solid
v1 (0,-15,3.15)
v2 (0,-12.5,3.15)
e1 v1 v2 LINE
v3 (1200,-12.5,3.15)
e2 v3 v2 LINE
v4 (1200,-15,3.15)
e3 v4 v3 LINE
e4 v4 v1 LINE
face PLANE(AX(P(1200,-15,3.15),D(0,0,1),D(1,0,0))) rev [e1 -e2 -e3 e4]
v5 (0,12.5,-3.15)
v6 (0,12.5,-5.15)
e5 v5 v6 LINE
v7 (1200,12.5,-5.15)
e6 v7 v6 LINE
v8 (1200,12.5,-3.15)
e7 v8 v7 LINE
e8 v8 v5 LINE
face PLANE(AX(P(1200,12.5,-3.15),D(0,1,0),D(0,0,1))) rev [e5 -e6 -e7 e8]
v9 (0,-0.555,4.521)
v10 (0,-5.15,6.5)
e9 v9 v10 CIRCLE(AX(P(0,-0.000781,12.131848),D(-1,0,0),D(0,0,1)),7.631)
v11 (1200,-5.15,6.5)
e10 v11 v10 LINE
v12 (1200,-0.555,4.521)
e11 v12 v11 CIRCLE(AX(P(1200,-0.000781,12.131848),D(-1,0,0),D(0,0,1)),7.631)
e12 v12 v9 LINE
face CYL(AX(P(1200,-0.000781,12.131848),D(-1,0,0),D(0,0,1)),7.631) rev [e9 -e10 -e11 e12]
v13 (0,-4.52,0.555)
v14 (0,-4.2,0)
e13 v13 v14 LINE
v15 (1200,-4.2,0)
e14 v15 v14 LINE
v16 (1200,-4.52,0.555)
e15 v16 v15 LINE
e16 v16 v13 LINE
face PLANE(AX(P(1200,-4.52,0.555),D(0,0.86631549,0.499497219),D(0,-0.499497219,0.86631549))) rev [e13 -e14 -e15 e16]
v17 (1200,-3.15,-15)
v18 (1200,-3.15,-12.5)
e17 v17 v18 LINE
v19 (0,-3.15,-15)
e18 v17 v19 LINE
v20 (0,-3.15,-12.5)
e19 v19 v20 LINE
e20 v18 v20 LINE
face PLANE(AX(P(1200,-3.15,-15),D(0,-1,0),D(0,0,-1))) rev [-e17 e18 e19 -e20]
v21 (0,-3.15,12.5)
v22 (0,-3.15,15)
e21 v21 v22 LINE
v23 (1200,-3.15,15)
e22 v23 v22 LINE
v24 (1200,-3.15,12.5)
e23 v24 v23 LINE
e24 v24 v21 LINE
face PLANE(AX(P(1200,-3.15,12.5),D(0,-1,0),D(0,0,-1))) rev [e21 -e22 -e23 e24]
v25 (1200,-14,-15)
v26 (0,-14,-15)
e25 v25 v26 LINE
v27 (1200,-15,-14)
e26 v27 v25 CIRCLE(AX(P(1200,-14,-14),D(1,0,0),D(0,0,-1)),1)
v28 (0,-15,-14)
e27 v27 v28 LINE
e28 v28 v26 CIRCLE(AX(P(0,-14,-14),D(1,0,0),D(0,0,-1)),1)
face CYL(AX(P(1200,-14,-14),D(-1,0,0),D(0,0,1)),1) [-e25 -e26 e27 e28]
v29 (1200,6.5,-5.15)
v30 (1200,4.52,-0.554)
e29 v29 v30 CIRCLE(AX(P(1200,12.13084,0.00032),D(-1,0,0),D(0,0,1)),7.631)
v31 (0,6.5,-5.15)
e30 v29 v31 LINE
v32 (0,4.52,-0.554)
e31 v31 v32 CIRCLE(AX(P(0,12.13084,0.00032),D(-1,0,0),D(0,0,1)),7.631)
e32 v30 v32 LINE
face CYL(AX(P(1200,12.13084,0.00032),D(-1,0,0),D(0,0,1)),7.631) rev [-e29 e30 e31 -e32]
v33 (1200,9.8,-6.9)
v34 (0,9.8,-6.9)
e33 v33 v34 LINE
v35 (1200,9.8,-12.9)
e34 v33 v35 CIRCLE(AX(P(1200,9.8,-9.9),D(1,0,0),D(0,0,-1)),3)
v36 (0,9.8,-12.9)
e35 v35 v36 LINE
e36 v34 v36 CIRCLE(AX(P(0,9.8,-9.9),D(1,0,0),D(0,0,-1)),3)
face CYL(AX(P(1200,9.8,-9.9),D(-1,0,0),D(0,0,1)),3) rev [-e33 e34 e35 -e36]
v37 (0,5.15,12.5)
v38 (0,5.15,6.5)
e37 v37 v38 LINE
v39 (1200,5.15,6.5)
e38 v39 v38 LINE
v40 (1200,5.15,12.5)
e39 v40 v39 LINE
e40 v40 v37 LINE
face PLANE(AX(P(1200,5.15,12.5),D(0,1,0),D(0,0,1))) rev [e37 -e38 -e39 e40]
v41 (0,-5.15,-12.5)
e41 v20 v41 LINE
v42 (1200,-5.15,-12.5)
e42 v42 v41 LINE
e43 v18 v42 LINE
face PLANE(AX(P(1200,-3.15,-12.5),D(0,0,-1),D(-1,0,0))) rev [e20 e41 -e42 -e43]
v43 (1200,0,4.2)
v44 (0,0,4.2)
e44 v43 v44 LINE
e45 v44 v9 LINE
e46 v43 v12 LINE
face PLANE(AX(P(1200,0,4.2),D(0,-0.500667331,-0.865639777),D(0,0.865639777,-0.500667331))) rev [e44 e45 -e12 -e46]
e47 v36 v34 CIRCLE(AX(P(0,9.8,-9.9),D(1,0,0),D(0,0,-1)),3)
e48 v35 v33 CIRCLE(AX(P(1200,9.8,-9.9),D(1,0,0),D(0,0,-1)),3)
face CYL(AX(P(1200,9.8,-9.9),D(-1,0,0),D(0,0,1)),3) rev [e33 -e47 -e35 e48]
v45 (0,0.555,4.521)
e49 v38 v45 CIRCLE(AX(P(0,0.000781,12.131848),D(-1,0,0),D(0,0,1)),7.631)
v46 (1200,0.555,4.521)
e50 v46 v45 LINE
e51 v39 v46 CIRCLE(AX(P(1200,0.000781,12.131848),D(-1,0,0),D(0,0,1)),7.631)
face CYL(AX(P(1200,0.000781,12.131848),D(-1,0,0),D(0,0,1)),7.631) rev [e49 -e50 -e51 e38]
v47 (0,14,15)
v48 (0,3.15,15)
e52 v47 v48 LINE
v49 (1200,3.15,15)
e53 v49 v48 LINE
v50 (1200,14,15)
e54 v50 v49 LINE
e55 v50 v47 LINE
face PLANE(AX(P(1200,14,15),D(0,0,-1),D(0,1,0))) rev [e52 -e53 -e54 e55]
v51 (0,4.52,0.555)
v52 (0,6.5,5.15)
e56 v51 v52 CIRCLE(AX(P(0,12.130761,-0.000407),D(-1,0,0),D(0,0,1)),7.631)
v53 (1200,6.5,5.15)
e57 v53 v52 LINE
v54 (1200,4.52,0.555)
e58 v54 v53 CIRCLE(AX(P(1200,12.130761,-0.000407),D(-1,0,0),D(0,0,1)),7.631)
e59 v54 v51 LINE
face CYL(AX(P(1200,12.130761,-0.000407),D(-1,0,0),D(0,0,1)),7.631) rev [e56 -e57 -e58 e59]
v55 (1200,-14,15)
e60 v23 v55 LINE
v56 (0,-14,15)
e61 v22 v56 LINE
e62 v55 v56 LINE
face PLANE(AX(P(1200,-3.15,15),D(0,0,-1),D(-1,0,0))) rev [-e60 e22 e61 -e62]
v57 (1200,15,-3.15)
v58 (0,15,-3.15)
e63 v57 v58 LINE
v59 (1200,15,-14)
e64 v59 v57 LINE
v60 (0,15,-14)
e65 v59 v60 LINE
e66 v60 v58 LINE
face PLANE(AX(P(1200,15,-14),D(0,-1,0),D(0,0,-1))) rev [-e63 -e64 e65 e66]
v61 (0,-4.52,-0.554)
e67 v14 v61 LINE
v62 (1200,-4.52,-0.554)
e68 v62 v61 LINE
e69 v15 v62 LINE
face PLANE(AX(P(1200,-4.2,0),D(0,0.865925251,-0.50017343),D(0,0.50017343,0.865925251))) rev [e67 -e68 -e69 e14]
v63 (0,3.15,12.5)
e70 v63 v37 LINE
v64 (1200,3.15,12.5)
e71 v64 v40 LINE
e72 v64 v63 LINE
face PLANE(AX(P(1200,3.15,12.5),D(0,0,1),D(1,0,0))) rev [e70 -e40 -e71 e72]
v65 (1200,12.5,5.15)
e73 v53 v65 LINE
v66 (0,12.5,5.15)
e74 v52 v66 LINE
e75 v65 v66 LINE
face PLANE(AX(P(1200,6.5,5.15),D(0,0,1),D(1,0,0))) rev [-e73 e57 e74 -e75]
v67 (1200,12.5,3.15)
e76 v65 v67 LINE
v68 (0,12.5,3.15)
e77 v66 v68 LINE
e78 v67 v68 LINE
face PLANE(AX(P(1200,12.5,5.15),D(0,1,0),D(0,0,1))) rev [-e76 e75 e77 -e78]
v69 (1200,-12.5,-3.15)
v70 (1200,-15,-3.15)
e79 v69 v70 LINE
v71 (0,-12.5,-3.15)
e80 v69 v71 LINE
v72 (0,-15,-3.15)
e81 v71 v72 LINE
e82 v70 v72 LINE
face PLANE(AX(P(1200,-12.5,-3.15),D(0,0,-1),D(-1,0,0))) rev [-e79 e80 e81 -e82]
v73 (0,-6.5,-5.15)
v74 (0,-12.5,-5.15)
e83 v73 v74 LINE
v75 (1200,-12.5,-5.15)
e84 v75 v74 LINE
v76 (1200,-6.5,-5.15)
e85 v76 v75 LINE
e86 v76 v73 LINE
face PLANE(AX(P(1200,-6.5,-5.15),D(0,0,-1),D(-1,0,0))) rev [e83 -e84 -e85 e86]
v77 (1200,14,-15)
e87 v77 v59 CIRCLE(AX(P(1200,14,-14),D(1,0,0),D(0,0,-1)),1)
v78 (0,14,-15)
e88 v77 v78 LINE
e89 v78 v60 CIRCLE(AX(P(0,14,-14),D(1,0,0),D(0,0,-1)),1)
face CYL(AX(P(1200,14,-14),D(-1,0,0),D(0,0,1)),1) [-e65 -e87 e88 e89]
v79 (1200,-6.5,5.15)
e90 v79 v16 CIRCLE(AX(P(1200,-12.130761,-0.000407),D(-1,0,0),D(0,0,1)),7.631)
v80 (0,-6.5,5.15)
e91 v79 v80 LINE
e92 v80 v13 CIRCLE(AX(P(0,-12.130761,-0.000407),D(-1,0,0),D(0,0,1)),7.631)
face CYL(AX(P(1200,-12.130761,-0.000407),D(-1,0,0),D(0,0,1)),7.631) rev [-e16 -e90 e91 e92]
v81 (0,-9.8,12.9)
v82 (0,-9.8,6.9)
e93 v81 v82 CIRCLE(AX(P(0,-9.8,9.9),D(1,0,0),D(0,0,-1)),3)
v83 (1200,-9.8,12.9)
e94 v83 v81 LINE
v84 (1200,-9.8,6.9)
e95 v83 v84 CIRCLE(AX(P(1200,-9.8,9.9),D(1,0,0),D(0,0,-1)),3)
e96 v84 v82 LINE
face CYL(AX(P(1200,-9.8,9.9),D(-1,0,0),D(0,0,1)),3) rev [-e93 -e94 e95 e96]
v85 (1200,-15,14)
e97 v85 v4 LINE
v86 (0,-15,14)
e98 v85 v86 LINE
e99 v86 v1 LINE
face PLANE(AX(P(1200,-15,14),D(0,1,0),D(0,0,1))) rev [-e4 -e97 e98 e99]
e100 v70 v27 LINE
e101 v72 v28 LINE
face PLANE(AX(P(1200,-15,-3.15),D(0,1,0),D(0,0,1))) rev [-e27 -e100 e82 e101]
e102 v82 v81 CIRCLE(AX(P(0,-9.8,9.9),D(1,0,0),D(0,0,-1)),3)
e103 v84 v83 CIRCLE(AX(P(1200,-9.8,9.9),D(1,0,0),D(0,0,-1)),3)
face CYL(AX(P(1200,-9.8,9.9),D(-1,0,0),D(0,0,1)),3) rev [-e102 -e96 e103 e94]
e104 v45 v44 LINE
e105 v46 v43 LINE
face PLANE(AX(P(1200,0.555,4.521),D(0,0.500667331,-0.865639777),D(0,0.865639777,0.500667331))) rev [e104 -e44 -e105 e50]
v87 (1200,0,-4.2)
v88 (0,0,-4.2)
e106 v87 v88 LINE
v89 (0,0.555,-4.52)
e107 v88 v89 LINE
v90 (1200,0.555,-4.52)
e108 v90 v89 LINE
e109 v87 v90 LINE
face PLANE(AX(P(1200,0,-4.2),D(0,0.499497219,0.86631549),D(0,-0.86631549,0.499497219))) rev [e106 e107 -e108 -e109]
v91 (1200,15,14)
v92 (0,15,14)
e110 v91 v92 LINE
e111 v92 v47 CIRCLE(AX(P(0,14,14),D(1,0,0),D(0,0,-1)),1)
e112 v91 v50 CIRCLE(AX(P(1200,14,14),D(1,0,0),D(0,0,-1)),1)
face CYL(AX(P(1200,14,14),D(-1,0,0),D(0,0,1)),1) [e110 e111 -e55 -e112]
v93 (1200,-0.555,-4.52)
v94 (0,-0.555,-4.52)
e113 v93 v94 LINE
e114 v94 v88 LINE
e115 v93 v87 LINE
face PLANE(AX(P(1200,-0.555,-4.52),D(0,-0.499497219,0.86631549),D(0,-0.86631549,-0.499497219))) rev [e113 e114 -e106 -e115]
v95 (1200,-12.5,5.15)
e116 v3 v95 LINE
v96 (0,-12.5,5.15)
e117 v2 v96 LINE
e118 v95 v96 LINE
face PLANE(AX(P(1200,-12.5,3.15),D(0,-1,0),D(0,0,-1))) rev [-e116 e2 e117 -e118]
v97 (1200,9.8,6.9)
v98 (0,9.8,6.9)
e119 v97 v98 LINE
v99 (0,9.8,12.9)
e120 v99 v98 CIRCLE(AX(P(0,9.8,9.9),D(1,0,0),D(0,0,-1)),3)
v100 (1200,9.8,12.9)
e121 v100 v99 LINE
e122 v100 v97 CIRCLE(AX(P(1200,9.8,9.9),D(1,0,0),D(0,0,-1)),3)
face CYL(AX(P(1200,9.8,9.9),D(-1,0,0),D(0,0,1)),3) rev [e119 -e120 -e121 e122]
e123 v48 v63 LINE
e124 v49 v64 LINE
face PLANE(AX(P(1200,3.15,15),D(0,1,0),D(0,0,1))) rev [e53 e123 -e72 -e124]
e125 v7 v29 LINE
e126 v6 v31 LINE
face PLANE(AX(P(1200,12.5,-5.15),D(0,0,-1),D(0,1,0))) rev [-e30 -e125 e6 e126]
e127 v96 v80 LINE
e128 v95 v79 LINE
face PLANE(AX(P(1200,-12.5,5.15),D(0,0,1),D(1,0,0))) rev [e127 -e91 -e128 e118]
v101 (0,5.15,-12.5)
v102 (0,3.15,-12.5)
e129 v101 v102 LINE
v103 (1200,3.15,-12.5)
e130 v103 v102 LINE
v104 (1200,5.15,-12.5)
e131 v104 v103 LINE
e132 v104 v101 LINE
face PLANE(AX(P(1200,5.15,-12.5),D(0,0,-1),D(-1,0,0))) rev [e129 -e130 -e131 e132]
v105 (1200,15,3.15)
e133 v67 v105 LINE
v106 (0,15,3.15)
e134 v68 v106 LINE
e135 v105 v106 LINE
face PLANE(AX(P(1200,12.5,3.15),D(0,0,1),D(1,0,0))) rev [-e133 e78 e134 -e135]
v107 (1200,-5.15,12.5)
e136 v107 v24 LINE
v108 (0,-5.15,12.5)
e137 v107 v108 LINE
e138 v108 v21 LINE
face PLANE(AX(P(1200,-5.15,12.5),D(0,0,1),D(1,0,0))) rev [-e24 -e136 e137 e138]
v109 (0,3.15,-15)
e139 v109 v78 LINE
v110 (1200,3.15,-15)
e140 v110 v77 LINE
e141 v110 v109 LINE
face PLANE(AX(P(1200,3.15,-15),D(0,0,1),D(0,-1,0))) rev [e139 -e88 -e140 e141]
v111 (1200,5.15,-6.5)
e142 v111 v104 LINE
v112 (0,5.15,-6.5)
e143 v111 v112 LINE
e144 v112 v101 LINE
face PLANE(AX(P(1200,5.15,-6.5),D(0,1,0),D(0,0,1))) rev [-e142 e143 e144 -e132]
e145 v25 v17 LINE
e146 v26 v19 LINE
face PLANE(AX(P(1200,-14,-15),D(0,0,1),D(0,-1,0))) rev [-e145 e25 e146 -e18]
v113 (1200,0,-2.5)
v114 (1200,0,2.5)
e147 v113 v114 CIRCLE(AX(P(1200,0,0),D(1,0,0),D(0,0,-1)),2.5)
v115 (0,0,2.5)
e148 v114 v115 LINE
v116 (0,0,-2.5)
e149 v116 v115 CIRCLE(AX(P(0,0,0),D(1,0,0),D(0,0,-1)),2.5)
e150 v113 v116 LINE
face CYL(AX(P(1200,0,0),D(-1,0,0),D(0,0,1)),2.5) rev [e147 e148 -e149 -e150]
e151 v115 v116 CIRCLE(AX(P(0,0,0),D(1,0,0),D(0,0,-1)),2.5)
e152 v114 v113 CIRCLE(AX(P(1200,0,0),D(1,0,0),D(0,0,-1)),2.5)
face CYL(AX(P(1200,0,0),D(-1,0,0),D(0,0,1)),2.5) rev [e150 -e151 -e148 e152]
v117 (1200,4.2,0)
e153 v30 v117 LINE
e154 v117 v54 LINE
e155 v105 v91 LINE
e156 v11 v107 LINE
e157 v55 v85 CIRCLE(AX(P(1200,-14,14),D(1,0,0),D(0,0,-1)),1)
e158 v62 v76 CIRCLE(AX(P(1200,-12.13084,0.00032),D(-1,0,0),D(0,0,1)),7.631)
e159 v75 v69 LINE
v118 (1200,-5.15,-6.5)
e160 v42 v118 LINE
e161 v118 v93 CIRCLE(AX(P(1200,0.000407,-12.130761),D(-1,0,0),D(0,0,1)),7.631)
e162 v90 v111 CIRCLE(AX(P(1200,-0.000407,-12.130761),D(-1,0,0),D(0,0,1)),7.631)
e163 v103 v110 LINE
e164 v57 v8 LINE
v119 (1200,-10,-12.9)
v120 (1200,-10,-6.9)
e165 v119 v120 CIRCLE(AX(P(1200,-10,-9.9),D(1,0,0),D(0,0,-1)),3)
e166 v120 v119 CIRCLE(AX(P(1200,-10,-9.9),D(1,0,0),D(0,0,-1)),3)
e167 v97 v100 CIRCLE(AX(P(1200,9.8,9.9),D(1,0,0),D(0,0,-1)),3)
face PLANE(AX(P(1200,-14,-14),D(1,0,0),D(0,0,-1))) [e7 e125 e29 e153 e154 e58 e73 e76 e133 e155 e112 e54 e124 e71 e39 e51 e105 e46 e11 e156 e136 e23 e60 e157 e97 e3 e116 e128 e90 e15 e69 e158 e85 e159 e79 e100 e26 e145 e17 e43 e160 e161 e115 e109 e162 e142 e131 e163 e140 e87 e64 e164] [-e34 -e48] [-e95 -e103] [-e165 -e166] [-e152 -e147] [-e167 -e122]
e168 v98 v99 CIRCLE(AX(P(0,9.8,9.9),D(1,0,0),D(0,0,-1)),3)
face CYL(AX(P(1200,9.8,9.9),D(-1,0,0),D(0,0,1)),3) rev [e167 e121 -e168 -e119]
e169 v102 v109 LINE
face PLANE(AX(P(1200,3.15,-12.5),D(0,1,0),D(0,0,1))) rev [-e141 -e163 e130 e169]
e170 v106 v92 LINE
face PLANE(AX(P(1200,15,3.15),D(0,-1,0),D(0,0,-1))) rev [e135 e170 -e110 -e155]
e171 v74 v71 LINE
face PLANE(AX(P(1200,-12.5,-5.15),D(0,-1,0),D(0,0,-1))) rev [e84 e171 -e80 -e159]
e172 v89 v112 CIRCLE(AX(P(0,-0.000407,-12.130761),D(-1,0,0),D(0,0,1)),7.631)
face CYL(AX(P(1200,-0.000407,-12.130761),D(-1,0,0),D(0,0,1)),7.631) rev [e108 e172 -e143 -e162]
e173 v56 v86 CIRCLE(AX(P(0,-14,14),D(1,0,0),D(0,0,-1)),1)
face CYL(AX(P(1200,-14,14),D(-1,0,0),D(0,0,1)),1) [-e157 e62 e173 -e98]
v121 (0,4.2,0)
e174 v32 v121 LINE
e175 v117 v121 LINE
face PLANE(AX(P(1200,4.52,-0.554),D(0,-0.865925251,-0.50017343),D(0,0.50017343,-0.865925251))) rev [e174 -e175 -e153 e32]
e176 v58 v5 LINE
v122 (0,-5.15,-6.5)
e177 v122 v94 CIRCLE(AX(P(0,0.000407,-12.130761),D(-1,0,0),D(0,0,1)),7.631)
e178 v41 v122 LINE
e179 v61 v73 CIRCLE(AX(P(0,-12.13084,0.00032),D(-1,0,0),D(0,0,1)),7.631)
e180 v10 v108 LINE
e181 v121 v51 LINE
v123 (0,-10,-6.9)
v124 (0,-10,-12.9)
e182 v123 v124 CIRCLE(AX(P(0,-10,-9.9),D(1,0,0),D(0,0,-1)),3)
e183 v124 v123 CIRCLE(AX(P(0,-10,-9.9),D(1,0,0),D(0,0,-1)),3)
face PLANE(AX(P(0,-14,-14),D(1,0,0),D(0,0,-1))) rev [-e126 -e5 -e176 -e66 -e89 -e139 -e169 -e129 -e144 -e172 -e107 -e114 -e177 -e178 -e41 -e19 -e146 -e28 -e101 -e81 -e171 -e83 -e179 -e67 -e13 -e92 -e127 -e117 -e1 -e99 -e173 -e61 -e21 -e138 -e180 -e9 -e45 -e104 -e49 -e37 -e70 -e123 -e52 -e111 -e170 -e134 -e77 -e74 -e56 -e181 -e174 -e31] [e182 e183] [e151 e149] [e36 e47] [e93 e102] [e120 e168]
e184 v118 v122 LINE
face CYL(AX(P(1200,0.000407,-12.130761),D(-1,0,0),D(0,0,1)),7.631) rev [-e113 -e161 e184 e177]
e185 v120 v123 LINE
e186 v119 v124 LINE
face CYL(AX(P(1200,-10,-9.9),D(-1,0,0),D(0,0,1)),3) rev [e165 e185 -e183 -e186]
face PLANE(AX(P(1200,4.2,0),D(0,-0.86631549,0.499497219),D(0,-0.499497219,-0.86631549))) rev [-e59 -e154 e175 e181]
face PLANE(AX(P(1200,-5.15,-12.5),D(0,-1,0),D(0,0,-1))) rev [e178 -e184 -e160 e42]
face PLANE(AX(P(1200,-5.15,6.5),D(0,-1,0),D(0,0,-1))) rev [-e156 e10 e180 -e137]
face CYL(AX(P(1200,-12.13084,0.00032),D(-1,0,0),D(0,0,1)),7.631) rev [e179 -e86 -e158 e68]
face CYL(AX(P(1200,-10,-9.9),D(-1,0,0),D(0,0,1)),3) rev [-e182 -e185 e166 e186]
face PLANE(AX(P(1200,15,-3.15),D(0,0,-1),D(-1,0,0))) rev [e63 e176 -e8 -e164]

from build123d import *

# Parameters (mm, degrees)
SKETCH_11_R         = 3
SKETCH_11_R_2       = 2.5
F_0_GY_3030_1_DEPTH = 1200


with BuildPart() as part:
    # 草图11 → 0国耀铝型材 GY-3030国标铝型材(1) (new body)
    with BuildSketch(Plane.YZ):
        with BuildLine():
            Line((-14, -15), (-3.15, -15))
            Line((-3.15, -15), (-3.15, -12.5))
            Line((-3.15, -12.5), (-5.15, -12.5))
            Line((-5.15, -12.5), (-5.15, -6.5))
            ThreePointArc((-5.15, -6.5), (-3.019390742, -5.122695475), (-0.555, -4.52))
            Line((-0.555, -4.52), (0, -4.2))
            Line((0, -4.2), (0.555, -4.52))
            ThreePointArc((0.555, -4.52), (3.019390742, -5.122695475), (5.15, -6.5))
            Line((5.15, -6.5), (5.15, -12.5))
            Line((5.15, -12.5), (3.15, -12.5))
            Line((3.15, -12.5), (3.15, -15))
            Line((3.15, -15), (14, -15))
            ThreePointArc((14, -15), (14.707106781, -14.707106781), (15, -14))
            Line((15, -14), (15, -3.15))
            Line((15, -3.15), (12.5, -3.15))
            Line((12.5, -3.15), (12.5, -5.15))
            Line((12.5, -5.15), (6.5, -5.15))
            ThreePointArc((6.5, -5.15), (5.12253592, -3.018923167), (4.52, -0.554))
            Line((4.52, -0.554), (4.2, 0))
            Line((4.2, 0), (4.52, 0.555))
            ThreePointArc((4.52, 0.555), (5.122695475, 3.019390742), (6.5, 5.15))
            Line((6.5, 5.15), (12.5, 5.15))
            Line((12.5, 5.15), (12.5, 3.15))
            Line((12.5, 3.15), (15, 3.15))
            Line((15, 3.15), (15, 14))
            ThreePointArc((15, 14), (14.707106781, 14.707106781), (14, 15))
            Line((14, 15), (3.15, 15))
            Line((3.15, 15), (3.15, 12.5))
            Line((3.15, 12.5), (5.15, 12.5))
            Line((5.15, 12.5), (5.15, 6.5))
            ThreePointArc((5.15, 6.5), (3.019292492, 5.123227892), (0.555, 4.521))
            Line((0.555, 4.521), (0, 4.2))
            Line((0, 4.2), (-0.555, 4.521))
            ThreePointArc((-0.555, 4.521), (-3.019292492, 5.123227892), (-5.15, 6.5))
            Line((-5.15, 6.5), (-5.15, 12.5))
            Line((-5.15, 12.5), (-3.15, 12.5))
            Line((-3.15, 12.5), (-3.15, 15))
            Line((-3.15, 15), (-14, 15))
            ThreePointArc((-14, 15), (-14.707106781, 14.707106781), (-15, 14))
            Line((-15, 14), (-15, 3.15))
            Line((-15, 3.15), (-12.5, 3.15))
            Line((-12.5, 3.15), (-12.5, 5.15))
            Line((-12.5, 5.15), (-6.5, 5.15))
            ThreePointArc((-6.5, 5.15), (-5.122695475, 3.019390742), (-4.52, 0.555))
            Line((-4.52, 0.555), (-4.2, 0))
            Line((-4.2, 0), (-4.52, -0.554))
            ThreePointArc((-4.52, -0.554), (-5.12253592, -3.018923167), (-6.5, -5.15))
            Line((-6.5, -5.15), (-12.5, -5.15))
            Line((-12.5, -5.15), (-12.5, -3.15))
            Line((-12.5, -3.15), (-15, -3.15))
            Line((-15, -3.15), (-15, -14))
            ThreePointArc((-15, -14), (-14.707106781, -14.707106781), (-14, -15))
        make_face()
        with Locations((9.8, 9.9)):
            Circle(SKETCH_11_R, mode=Mode.SUBTRACT)
        with Locations((9.8, -9.9)):
            Circle(SKETCH_11_R, mode=Mode.SUBTRACT)
        Circle(SKETCH_11_R_2, mode=Mode.SUBTRACT)
        with Locations((-9.8, 9.9)):
            Circle(SKETCH_11_R, mode=Mode.SUBTRACT)
        with Locations((-10, -9.9)):
            Circle(SKETCH_11_R, mode=Mode.SUBTRACT)
    extrude(amount=F_0_GY_3030_1_DEPTH)


solid = part.part
